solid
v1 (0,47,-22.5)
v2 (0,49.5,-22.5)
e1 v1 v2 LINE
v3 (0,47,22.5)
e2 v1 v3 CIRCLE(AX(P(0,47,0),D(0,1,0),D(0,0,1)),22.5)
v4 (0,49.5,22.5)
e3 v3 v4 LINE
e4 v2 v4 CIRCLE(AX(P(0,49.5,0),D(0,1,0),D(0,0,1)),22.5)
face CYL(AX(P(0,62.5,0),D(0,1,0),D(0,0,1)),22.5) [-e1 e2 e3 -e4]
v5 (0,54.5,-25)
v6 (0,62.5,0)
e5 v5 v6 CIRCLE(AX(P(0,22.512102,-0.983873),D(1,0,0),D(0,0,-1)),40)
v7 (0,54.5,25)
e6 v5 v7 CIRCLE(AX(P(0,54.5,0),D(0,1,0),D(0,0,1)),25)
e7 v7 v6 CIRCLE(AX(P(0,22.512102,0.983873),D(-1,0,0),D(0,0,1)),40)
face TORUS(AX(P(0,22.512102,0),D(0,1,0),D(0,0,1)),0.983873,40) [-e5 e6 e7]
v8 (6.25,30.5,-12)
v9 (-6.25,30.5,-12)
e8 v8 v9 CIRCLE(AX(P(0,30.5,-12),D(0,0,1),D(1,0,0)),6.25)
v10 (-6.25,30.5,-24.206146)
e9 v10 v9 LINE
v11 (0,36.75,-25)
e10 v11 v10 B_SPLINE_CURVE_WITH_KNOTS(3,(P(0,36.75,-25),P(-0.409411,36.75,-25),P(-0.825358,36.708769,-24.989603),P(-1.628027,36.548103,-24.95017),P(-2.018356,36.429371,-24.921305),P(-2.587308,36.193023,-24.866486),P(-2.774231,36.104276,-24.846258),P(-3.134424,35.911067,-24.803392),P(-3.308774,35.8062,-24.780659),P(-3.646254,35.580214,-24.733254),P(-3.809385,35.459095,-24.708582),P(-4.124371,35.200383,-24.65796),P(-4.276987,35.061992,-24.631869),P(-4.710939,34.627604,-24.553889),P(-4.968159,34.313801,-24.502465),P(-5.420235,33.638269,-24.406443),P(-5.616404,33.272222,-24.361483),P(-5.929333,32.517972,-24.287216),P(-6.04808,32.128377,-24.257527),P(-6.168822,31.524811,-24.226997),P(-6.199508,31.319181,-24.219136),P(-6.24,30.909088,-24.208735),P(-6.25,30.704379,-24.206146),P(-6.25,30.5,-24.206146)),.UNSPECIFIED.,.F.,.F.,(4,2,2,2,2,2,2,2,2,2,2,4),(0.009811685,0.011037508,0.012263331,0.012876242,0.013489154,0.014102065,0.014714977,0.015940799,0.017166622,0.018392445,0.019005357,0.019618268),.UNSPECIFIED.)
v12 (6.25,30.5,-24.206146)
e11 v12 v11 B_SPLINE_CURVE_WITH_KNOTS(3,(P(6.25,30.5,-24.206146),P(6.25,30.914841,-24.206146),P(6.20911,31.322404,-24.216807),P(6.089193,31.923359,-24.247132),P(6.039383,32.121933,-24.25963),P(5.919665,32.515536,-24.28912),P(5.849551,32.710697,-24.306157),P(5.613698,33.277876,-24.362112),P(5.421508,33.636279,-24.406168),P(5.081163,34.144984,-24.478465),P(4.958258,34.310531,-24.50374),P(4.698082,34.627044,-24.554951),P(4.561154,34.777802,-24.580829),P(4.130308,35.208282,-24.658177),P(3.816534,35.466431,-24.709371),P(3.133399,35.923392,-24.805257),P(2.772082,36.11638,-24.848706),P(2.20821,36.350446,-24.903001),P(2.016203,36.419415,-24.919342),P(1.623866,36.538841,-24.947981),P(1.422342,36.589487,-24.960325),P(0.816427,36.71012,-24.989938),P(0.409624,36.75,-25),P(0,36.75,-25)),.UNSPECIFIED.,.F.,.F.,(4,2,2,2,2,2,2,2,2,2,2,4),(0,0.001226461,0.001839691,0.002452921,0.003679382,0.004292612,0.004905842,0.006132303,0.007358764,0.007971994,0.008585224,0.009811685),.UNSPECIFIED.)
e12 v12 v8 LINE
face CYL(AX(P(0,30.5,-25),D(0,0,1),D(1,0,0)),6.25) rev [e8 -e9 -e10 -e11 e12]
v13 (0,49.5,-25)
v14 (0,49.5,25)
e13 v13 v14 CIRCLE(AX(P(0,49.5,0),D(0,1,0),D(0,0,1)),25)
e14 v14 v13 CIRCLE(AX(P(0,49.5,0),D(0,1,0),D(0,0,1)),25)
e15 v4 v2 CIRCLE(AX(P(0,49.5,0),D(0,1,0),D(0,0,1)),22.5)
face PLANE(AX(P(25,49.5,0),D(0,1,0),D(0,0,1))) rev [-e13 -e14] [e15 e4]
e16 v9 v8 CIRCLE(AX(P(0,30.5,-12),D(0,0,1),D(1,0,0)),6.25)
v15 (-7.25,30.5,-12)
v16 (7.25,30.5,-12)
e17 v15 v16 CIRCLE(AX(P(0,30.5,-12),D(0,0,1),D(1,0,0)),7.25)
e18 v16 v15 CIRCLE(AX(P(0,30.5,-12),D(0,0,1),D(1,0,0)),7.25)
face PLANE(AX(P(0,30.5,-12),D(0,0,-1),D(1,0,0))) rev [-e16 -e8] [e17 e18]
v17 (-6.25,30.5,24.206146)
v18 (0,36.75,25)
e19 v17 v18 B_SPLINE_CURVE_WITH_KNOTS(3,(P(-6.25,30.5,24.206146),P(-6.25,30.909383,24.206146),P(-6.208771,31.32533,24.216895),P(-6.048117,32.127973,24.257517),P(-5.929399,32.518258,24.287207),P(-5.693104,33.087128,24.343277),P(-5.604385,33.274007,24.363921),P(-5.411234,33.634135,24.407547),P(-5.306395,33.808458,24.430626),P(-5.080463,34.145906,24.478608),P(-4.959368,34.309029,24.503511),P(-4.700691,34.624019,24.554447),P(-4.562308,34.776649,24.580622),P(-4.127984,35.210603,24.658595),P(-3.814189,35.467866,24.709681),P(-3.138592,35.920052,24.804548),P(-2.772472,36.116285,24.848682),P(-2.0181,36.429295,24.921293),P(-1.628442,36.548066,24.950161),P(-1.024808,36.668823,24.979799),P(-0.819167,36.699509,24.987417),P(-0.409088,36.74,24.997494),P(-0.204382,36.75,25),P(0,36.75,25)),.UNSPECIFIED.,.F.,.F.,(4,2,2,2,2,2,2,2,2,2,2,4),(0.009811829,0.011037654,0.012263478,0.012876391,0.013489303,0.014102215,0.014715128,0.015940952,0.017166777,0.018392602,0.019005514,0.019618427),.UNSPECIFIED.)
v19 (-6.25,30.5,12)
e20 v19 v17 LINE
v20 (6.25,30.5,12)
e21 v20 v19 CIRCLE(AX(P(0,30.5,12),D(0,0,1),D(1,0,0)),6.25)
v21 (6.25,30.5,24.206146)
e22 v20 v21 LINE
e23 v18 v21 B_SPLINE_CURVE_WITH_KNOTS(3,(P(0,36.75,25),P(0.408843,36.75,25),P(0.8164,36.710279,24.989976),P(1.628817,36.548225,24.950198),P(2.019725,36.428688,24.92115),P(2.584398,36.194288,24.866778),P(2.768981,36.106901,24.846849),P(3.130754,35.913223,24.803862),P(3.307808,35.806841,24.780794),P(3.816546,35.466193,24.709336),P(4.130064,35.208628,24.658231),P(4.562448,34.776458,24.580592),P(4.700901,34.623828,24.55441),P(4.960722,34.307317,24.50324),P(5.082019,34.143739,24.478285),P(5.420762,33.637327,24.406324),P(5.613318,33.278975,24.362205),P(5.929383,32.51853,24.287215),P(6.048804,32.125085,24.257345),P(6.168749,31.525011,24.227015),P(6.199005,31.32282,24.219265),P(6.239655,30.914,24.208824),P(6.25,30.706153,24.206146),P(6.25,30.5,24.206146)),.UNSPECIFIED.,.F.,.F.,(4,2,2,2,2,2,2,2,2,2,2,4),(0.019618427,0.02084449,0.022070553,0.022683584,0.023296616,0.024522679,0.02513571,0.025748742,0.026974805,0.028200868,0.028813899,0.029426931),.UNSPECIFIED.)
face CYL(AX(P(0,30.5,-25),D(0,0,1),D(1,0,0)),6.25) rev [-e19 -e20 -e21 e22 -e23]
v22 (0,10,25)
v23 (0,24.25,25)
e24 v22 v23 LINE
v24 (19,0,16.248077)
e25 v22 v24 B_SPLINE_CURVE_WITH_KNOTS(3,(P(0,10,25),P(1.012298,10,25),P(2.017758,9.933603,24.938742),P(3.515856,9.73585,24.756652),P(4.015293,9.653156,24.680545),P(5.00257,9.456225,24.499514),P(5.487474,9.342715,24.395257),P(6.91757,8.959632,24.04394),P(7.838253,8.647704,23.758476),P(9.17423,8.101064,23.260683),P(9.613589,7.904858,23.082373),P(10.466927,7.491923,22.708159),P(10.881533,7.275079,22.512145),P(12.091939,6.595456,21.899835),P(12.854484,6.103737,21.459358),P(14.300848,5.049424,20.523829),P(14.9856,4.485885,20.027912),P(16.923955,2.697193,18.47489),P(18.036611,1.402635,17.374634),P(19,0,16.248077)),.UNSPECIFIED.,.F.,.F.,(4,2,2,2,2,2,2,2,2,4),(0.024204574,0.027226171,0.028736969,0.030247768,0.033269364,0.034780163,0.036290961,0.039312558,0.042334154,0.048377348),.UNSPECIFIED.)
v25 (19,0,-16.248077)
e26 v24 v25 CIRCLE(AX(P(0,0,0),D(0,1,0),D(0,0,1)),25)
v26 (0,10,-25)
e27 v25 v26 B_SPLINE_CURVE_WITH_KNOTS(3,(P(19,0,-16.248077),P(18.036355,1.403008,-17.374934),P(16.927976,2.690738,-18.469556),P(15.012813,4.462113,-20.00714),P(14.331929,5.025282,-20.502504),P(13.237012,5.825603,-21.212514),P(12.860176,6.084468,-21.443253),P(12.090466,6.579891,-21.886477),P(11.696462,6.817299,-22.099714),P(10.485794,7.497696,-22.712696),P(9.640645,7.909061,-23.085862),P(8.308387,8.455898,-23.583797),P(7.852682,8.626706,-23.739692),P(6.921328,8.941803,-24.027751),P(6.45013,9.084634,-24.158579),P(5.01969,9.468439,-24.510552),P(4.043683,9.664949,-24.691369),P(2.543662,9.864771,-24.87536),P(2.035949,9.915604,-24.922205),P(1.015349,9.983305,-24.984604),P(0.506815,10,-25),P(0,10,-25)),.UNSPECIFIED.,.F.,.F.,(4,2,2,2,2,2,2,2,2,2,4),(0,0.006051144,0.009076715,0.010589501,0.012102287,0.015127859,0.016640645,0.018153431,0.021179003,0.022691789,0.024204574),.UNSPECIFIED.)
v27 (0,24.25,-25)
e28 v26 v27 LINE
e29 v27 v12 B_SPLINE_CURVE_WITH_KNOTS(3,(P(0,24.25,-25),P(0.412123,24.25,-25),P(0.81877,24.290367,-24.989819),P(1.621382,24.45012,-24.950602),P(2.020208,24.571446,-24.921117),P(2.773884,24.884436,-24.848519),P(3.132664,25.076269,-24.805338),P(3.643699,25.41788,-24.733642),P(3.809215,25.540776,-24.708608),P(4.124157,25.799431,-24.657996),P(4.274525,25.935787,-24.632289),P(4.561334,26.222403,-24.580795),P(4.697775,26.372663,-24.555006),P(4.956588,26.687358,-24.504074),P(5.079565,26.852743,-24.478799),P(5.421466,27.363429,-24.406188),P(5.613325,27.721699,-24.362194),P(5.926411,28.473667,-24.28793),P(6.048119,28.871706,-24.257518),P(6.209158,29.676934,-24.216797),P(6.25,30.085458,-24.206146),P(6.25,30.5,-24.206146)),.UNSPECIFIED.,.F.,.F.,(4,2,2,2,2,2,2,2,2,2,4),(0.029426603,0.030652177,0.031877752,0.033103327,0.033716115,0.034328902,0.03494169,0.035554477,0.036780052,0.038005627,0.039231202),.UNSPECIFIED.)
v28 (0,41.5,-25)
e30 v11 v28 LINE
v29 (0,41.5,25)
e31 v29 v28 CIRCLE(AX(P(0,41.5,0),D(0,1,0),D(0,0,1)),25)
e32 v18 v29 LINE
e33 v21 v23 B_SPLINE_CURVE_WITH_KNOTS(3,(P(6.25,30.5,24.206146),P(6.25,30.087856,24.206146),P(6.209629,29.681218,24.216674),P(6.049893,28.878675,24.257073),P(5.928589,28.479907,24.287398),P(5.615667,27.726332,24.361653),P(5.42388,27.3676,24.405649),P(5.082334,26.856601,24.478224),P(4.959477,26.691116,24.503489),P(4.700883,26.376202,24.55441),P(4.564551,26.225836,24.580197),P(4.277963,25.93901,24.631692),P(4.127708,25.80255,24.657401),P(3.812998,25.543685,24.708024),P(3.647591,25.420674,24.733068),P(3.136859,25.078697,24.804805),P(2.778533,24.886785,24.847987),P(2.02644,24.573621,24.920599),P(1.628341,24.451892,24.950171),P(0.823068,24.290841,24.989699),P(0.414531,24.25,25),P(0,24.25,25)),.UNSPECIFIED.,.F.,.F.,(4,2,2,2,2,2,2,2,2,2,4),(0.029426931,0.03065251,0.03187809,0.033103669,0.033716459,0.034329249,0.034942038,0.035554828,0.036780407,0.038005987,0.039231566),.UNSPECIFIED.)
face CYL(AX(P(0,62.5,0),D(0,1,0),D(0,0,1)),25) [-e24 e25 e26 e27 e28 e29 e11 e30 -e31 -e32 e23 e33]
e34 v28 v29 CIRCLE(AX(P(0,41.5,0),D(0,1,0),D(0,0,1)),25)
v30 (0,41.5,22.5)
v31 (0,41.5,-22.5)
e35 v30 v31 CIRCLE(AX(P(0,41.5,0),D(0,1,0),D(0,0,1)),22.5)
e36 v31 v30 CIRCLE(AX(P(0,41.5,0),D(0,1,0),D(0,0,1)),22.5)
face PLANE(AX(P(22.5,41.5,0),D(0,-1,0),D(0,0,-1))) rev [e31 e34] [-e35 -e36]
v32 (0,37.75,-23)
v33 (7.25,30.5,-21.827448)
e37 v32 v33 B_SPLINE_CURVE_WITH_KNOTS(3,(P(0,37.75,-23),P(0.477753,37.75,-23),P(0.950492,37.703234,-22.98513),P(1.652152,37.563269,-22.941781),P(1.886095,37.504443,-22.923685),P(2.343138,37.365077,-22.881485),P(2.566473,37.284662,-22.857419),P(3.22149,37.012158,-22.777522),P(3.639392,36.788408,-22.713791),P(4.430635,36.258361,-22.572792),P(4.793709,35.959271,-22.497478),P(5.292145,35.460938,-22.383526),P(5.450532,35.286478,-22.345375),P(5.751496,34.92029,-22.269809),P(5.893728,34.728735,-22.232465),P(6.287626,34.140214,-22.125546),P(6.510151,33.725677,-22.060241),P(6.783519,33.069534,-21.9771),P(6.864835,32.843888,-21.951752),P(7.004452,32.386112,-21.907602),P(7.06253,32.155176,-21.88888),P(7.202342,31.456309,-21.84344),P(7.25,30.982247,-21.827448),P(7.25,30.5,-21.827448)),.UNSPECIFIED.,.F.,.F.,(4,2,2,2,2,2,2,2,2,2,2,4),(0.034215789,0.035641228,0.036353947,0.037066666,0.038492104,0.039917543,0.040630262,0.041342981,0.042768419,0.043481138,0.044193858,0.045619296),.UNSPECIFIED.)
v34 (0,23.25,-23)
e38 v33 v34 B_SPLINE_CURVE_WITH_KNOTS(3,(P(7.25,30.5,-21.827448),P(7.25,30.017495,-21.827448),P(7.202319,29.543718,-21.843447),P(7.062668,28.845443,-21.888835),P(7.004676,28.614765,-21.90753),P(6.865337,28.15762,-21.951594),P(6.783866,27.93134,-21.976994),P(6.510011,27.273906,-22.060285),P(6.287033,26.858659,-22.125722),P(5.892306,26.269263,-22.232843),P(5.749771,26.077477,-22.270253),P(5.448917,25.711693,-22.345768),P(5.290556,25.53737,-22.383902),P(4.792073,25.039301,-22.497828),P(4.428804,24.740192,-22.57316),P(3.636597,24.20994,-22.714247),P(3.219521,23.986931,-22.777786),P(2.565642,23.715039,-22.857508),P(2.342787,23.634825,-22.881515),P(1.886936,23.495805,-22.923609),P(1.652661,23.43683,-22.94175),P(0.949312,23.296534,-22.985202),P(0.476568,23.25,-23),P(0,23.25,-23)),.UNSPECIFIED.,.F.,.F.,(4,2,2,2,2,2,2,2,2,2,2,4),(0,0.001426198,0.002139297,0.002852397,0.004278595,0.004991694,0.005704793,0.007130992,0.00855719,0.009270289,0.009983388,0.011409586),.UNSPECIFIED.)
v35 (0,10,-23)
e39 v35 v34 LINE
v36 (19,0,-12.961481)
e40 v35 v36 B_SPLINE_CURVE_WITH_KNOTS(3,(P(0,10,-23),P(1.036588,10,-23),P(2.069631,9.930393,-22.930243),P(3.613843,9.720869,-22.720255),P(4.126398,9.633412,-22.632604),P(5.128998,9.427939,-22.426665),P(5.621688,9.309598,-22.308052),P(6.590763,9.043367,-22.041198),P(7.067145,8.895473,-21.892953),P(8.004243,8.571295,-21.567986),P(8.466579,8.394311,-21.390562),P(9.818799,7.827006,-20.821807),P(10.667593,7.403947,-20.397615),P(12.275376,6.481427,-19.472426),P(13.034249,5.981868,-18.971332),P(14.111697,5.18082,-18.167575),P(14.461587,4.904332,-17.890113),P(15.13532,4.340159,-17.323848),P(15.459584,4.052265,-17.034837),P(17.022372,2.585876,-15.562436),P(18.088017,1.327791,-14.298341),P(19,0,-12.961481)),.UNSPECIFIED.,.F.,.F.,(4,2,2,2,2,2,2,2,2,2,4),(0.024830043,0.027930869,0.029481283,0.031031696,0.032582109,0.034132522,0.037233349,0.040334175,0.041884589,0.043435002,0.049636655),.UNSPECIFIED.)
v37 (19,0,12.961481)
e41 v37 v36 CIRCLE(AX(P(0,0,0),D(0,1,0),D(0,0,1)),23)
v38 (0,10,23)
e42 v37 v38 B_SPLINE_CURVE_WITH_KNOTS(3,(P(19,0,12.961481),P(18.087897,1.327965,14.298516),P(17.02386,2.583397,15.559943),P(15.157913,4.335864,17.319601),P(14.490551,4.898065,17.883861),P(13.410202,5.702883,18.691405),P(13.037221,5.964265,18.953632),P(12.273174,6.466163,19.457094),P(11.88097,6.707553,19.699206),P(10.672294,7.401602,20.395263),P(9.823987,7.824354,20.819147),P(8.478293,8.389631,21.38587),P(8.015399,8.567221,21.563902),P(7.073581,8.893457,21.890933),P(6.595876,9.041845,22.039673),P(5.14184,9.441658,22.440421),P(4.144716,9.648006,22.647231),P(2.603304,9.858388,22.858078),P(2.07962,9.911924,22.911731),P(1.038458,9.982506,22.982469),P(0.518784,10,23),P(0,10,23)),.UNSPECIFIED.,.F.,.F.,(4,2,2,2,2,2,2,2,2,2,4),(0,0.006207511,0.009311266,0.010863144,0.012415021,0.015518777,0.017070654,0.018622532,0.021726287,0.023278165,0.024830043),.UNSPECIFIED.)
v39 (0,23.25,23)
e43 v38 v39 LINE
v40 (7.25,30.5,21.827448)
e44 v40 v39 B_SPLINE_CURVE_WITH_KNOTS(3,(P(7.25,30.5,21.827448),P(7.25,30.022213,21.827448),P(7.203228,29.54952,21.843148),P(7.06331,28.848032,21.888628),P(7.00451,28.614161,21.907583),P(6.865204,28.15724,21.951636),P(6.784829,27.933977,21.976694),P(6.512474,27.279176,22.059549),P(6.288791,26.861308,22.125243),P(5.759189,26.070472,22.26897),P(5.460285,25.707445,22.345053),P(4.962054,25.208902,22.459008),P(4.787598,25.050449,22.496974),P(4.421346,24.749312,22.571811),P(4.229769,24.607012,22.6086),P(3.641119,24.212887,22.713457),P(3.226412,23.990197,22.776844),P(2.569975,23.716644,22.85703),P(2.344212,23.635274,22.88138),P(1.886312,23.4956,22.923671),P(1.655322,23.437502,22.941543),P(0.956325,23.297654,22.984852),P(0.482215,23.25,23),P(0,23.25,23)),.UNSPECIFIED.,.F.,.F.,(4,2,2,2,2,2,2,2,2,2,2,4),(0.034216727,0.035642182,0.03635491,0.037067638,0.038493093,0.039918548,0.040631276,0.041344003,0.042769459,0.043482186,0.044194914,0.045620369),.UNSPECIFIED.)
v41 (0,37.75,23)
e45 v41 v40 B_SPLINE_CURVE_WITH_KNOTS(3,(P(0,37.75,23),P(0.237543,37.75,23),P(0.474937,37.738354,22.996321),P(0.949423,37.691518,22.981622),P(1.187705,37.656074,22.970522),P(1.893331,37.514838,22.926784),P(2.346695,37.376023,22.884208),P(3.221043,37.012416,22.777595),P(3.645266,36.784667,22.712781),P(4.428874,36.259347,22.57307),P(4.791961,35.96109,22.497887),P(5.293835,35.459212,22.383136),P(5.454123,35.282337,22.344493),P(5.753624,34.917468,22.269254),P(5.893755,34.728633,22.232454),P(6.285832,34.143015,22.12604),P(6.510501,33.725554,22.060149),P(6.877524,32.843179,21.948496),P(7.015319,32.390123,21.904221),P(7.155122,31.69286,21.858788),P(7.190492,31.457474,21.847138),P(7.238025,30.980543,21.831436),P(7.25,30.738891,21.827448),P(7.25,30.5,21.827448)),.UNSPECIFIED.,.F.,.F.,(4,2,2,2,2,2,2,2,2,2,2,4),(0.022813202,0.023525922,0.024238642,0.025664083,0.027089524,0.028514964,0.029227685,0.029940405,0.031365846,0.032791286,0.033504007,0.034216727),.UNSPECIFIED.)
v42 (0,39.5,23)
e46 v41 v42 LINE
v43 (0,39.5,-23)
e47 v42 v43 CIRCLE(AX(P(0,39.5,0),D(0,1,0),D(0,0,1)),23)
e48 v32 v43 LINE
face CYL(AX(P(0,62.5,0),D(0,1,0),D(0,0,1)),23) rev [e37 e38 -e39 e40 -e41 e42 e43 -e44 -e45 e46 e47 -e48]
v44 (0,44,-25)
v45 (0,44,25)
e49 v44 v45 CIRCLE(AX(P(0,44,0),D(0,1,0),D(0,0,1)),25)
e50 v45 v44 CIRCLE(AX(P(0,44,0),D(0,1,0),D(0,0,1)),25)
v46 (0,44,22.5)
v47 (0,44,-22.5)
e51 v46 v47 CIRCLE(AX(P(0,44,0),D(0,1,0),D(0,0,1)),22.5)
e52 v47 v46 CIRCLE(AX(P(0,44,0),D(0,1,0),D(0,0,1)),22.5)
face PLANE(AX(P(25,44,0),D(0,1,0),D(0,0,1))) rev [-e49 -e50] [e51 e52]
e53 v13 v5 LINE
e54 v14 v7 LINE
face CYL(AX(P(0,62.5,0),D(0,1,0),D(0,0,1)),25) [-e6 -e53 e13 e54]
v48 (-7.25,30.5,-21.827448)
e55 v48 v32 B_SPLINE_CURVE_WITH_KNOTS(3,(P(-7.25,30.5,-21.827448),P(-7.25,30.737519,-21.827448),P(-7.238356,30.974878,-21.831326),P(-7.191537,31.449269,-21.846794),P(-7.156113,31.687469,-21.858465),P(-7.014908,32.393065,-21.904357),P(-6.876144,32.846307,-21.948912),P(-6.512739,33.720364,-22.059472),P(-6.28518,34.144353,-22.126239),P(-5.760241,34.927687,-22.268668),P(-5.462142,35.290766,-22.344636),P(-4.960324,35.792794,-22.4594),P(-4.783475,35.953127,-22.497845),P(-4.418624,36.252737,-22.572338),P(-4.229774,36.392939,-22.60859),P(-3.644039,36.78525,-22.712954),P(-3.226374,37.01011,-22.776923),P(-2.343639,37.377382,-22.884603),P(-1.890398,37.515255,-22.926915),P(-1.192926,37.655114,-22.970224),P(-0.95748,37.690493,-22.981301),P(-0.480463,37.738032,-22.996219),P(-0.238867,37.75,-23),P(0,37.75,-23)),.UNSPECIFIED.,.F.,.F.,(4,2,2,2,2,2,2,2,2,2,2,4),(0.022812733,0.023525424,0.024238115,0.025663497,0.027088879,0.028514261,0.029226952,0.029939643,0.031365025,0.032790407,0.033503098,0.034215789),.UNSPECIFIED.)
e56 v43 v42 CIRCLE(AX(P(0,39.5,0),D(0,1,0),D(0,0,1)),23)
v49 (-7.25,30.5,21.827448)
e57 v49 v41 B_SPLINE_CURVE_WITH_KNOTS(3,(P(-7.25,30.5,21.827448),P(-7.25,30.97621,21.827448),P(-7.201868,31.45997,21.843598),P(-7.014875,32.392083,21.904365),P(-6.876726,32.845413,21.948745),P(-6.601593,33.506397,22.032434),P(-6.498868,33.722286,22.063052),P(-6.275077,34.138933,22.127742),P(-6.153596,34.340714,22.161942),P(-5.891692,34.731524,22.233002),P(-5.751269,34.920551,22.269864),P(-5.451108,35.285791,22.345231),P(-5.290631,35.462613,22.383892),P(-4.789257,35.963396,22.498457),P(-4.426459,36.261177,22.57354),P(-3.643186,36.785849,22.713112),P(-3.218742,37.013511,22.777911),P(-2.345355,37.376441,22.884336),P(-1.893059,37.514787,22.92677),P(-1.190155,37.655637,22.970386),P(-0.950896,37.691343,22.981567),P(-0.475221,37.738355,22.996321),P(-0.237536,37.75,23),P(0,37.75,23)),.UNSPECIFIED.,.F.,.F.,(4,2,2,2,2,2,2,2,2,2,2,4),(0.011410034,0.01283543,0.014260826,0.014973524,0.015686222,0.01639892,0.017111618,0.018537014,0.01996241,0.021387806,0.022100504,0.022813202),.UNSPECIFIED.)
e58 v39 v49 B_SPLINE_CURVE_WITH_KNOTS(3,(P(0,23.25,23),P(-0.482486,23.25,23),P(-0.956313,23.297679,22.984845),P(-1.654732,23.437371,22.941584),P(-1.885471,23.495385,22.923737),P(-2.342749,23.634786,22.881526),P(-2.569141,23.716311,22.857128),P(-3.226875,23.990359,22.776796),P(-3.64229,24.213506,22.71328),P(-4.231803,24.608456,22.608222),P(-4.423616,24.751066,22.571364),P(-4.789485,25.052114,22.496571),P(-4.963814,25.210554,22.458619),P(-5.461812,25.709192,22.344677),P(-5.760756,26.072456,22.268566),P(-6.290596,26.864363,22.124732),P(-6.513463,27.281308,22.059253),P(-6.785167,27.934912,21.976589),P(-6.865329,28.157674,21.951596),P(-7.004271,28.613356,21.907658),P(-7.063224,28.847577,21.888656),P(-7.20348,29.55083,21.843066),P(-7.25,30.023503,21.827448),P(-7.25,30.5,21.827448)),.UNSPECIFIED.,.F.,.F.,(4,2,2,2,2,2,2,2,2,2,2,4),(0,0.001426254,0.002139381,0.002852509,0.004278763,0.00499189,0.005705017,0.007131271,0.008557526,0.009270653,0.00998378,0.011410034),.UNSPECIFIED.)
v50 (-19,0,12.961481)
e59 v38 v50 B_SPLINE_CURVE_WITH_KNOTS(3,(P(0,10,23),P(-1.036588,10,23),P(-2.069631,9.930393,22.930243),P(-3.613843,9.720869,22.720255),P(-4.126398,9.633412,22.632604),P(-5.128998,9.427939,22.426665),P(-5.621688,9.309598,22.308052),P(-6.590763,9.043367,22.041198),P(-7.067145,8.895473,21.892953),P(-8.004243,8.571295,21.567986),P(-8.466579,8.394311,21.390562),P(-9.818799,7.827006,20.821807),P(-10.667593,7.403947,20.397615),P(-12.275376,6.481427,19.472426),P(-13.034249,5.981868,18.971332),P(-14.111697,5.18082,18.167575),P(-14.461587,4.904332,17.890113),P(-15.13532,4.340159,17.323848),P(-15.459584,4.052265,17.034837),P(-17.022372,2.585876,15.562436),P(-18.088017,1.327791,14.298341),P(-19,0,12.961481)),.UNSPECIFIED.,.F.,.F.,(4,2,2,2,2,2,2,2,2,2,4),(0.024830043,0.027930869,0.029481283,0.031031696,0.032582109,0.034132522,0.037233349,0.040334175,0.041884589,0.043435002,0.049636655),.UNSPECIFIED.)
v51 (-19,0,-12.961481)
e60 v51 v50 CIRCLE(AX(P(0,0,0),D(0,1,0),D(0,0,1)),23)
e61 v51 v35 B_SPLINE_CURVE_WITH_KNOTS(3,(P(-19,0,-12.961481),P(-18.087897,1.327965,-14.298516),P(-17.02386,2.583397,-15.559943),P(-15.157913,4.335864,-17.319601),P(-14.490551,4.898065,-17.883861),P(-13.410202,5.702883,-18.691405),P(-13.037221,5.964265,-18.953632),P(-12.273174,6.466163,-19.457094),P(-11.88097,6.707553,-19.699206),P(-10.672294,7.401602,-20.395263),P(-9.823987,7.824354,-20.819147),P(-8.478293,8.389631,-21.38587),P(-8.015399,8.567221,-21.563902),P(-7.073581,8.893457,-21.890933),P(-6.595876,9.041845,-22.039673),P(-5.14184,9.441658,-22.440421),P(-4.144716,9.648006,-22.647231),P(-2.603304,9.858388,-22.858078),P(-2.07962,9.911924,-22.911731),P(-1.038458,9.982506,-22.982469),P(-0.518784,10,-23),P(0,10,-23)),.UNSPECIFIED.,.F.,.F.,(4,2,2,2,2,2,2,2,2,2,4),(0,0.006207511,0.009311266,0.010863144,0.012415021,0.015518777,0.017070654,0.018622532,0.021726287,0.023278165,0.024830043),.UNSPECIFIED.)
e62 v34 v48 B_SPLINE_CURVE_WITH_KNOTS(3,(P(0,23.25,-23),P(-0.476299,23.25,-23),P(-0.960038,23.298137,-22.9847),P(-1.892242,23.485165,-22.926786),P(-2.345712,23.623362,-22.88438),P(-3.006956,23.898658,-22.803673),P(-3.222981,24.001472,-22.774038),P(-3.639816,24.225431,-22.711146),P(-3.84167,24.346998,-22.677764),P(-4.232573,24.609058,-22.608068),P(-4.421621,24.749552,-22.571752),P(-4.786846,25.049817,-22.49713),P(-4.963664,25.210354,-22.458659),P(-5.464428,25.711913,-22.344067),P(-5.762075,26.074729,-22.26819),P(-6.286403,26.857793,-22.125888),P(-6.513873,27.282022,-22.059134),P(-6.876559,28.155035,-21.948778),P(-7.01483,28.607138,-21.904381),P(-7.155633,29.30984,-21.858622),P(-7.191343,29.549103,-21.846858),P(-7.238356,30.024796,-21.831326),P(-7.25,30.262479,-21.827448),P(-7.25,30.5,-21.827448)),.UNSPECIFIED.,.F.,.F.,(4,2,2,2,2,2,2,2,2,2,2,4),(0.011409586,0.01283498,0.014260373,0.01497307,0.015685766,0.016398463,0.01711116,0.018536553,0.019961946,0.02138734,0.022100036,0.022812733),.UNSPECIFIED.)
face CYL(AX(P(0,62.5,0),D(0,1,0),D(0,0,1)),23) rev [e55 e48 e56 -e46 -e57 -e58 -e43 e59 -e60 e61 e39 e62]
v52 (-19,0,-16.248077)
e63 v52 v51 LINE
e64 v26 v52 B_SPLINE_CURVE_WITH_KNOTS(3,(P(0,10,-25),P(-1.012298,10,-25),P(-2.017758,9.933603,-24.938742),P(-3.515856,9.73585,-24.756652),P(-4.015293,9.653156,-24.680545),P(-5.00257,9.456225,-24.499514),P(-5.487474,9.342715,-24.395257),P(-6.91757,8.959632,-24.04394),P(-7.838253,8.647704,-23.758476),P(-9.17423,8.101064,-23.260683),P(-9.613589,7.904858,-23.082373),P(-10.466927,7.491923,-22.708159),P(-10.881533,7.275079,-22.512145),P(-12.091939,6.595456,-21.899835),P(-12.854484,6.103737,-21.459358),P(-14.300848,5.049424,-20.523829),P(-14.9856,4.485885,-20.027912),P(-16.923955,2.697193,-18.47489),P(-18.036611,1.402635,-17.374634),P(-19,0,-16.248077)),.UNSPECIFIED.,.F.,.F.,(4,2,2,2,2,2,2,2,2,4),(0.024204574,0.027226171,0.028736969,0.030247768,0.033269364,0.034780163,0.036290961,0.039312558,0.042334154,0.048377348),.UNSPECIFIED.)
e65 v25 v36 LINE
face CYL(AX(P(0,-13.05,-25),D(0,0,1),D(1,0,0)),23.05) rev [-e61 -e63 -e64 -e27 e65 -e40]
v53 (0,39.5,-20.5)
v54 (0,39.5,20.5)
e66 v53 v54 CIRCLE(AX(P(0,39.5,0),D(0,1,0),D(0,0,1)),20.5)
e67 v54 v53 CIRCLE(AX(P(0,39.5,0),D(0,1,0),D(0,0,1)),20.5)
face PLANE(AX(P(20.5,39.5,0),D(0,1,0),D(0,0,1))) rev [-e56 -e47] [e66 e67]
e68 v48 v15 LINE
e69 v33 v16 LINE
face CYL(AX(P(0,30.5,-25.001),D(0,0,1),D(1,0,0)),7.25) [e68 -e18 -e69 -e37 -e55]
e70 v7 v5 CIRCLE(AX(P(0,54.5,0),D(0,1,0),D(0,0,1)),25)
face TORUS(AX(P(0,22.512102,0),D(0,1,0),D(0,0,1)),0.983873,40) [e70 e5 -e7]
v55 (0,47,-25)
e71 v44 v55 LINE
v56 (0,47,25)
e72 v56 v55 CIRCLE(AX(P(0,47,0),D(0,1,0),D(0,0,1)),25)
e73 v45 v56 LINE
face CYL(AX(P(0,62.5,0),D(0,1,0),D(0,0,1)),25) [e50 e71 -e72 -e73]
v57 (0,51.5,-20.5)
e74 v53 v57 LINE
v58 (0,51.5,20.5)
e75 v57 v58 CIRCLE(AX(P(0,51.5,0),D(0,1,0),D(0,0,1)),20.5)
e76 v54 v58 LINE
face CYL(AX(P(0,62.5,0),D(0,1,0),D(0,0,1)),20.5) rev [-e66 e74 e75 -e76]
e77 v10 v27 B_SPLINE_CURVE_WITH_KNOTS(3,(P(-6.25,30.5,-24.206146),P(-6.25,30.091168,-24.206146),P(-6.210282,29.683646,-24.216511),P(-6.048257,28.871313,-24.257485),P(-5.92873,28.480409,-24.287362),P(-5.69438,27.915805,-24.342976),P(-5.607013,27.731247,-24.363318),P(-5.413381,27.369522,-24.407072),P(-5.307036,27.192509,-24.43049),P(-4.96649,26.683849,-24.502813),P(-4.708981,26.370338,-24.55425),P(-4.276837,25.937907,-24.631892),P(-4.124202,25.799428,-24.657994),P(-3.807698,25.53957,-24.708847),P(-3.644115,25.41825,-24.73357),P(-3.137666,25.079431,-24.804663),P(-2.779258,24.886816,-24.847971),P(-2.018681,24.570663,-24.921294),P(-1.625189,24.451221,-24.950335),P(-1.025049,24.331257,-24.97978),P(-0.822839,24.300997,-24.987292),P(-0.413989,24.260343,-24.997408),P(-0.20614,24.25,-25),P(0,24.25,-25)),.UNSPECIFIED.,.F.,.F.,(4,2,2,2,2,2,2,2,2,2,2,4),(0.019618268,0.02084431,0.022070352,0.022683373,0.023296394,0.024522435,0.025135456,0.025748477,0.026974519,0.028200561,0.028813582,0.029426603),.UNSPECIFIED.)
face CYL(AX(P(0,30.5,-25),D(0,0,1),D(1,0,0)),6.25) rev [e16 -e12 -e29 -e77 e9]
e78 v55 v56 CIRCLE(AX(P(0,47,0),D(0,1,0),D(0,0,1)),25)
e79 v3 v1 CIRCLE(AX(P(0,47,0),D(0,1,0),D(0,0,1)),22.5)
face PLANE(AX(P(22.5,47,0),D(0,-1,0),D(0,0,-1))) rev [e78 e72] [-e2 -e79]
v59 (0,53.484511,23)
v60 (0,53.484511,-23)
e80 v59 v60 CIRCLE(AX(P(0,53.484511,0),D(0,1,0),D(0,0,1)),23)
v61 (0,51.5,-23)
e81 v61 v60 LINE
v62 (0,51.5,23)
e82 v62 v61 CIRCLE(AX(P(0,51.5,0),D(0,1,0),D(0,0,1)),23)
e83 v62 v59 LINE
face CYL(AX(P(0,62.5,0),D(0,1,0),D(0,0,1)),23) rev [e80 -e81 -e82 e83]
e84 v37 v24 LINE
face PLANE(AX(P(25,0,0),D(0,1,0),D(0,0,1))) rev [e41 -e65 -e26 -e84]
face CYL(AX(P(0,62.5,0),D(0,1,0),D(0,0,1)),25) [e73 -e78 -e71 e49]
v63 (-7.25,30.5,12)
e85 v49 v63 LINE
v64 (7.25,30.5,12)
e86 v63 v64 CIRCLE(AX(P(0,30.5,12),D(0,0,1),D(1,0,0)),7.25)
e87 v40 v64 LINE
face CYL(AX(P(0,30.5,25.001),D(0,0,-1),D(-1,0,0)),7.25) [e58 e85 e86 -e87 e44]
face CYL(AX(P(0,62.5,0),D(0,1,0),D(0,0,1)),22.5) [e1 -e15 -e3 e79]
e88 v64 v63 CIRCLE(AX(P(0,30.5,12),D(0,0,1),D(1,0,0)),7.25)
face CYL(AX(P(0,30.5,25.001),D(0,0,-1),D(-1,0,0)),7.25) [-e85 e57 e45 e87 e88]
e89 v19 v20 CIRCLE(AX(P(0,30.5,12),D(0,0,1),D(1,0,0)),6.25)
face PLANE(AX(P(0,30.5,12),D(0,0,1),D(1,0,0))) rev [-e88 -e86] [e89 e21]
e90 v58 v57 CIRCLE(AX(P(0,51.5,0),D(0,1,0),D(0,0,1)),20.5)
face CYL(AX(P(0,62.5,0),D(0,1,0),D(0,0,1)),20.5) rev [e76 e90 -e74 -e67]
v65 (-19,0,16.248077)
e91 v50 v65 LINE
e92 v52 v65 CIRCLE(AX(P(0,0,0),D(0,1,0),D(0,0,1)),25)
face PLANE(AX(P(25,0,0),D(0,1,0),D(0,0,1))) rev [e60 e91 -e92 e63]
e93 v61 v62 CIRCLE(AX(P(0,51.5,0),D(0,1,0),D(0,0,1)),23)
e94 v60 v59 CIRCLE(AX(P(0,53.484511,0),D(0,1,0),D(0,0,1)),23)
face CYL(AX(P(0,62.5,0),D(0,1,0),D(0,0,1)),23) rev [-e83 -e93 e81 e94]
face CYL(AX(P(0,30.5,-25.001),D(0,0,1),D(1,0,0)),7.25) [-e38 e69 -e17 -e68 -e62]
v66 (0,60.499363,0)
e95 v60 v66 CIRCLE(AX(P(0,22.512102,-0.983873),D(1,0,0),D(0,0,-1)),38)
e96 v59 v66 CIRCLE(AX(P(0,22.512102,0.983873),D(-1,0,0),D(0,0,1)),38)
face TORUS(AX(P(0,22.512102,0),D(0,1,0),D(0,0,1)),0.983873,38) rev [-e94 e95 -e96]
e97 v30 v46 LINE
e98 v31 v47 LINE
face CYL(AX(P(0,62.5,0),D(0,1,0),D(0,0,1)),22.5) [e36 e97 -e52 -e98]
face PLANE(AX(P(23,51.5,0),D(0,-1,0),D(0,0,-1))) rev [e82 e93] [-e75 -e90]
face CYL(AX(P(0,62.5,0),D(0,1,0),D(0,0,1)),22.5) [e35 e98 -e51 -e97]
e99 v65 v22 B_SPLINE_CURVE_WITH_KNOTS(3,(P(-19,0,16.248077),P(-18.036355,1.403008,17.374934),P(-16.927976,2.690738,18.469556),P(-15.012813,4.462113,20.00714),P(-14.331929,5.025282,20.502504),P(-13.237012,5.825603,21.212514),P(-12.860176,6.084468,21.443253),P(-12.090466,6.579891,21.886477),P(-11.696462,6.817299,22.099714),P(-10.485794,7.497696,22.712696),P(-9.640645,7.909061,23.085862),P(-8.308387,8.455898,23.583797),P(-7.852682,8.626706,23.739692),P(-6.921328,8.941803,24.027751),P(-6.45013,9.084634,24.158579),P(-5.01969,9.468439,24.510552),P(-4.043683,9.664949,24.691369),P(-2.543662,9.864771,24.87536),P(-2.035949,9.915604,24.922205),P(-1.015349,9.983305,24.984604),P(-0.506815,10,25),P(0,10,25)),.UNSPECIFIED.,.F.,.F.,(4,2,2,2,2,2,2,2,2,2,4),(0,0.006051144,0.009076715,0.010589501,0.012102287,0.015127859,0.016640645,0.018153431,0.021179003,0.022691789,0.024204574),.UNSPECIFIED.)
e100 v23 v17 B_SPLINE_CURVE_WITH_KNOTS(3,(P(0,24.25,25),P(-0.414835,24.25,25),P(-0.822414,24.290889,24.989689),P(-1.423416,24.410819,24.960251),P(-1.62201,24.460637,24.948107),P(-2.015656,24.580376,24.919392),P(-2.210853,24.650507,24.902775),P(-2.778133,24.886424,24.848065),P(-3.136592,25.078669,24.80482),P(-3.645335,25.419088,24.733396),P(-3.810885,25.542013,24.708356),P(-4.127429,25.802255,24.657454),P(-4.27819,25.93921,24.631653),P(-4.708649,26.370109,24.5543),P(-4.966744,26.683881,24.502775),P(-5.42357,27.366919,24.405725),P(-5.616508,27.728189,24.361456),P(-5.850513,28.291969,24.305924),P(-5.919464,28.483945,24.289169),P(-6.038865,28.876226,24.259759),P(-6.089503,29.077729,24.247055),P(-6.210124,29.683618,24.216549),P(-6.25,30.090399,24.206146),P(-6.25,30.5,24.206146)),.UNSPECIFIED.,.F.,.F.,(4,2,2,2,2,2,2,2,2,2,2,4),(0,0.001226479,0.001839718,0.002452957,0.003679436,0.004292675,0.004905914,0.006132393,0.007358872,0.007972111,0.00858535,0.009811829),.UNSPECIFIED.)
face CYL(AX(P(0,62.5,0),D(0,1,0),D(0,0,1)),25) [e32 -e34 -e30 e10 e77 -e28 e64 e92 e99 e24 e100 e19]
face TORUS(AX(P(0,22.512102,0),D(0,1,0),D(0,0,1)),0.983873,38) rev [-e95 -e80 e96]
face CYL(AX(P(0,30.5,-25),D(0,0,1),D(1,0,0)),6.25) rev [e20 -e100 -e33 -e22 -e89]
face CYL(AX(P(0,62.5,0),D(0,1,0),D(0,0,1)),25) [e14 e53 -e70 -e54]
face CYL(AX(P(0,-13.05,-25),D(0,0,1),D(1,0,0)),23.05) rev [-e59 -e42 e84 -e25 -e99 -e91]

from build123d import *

# Parameters (mm, degrees)
SKIRT_RELIEF_CUT_DEPTH      = 72.817566835
SKIRT_RELIEF_CUT_DEPTH_BACK = 72.817566835
SKIRT_RELIEF_SKETCH_R       = 6.25
PIN_BOSS_REACH              = 85.818
PIN_BOSS_END_RADIUS         = 23
PIN_START                   = 12
PIN_BOSS_SKETCH_R           = 7.25
PIN_BOSS_SKETCH_R_2         = 6.25


with BuildPart() as part:
    # Piston Profile Sketch → Piston Body with Ring Grooves (revolve)
    with BuildSketch(Plane.XY, mode=Mode.PRIVATE) as piston_body_with_ring_grooves_sk:
        with BuildLine():
            Line((25, 0), (25, 41.5))
            Line((25, 41.5), (22.5, 41.5))
            Line((22.5, 41.5), (22.5, 44))
            Line((22.5, 44), (25, 44))
            Line((25, 44), (25, 47))
            Line((25, 47), (22.5, 47))
            Line((22.5, 47), (22.5, 49.5))
            Line((22.5, 49.5), (25, 49.5))
            Line((25, 49.5), (25, 54.5))
            ThreePointArc((25, 54.5), (13.174901691, 60.609067785), (0, 62.5))
            Line((0, 62.5), (0, 60.49936285))
            ThreePointArc((0, 60.49936285), (12.069492637, 58.859165445), (23, 53.484511145))
            Line((23, 53.484511145), (23, 51.5))
            Line((23, 51.5), (20.5, 51.5))
            Line((20.5, 51.5), (20.5, 45.5))
            Line((20.5, 45.5), (20.5, 39.5))
            Line((20.5, 39.5), (23, 39.5))
            Line((23, 39.5), (23, 0))
            Line((23, 0), (25, 0))
        make_face()
    revolve(piston_body_with_ring_grooves_sk.sketch.rotate(Axis((0, 62.5, 0), (0, -1, 0)), 90), axis=Axis((0, 62.5, 0), (0, -1, 0)))

    # Skirt Relief Sketch → Skirt Relief Cut (cut, two sides: drawn at the far end of the back side and taken through both)
    with BuildSketch(Plane.XY.offset(-SKIRT_RELIEF_CUT_DEPTH_BACK)):
        with Locations((0, 30.5)):
            Circle(SKIRT_RELIEF_SKETCH_R)
        with BuildLine():
            Line((-19, 0), (19, 0))
            ThreePointArc((19, 0), (0, 10), (-19, 0))
        make_face()
    extrude(amount=SKIRT_RELIEF_CUT_DEPTH + SKIRT_RELIEF_CUT_DEPTH_BACK, mode=Mode.SUBTRACT)

    # Pin Boss: up to this cylinder (the profile starts inside it)
    pin_boss_end = Plane(origin=(0, 23.455061, 0), z_dir=(0, 1, 0)) * Cylinder(PIN_BOSS_END_RADIUS, 218.636, mode=Mode.PRIVATE)
    # Pin Boss Sketch → Pin Boss (add, up to the surface)
    with BuildSketch(Plane.XY.offset(PIN_START), mode=Mode.PRIVATE) as pin_boss_sk1:
        with Locations(Location((0, 30.5, 0), (0, 0, 90))):
            Circle(PIN_BOSS_SKETCH_R)
        with Locations((0, 30.5)):
            Circle(PIN_BOSS_SKETCH_R_2, mode=Mode.SUBTRACT)
    pin_boss_tool1 = extrude(pin_boss_sk1.sketch, amount=PIN_BOSS_REACH, mode=Mode.PRIVATE) & pin_boss_end
    pin_boss = pin_boss_tool1.solids().sort_by_distance((0, 23.455061, 12))[0]
    add(pin_boss)

    # Pin Boss Mirror: Pin Boss across plane
    add(pin_boss.mirror(Plane.XY))


solid = part.part
